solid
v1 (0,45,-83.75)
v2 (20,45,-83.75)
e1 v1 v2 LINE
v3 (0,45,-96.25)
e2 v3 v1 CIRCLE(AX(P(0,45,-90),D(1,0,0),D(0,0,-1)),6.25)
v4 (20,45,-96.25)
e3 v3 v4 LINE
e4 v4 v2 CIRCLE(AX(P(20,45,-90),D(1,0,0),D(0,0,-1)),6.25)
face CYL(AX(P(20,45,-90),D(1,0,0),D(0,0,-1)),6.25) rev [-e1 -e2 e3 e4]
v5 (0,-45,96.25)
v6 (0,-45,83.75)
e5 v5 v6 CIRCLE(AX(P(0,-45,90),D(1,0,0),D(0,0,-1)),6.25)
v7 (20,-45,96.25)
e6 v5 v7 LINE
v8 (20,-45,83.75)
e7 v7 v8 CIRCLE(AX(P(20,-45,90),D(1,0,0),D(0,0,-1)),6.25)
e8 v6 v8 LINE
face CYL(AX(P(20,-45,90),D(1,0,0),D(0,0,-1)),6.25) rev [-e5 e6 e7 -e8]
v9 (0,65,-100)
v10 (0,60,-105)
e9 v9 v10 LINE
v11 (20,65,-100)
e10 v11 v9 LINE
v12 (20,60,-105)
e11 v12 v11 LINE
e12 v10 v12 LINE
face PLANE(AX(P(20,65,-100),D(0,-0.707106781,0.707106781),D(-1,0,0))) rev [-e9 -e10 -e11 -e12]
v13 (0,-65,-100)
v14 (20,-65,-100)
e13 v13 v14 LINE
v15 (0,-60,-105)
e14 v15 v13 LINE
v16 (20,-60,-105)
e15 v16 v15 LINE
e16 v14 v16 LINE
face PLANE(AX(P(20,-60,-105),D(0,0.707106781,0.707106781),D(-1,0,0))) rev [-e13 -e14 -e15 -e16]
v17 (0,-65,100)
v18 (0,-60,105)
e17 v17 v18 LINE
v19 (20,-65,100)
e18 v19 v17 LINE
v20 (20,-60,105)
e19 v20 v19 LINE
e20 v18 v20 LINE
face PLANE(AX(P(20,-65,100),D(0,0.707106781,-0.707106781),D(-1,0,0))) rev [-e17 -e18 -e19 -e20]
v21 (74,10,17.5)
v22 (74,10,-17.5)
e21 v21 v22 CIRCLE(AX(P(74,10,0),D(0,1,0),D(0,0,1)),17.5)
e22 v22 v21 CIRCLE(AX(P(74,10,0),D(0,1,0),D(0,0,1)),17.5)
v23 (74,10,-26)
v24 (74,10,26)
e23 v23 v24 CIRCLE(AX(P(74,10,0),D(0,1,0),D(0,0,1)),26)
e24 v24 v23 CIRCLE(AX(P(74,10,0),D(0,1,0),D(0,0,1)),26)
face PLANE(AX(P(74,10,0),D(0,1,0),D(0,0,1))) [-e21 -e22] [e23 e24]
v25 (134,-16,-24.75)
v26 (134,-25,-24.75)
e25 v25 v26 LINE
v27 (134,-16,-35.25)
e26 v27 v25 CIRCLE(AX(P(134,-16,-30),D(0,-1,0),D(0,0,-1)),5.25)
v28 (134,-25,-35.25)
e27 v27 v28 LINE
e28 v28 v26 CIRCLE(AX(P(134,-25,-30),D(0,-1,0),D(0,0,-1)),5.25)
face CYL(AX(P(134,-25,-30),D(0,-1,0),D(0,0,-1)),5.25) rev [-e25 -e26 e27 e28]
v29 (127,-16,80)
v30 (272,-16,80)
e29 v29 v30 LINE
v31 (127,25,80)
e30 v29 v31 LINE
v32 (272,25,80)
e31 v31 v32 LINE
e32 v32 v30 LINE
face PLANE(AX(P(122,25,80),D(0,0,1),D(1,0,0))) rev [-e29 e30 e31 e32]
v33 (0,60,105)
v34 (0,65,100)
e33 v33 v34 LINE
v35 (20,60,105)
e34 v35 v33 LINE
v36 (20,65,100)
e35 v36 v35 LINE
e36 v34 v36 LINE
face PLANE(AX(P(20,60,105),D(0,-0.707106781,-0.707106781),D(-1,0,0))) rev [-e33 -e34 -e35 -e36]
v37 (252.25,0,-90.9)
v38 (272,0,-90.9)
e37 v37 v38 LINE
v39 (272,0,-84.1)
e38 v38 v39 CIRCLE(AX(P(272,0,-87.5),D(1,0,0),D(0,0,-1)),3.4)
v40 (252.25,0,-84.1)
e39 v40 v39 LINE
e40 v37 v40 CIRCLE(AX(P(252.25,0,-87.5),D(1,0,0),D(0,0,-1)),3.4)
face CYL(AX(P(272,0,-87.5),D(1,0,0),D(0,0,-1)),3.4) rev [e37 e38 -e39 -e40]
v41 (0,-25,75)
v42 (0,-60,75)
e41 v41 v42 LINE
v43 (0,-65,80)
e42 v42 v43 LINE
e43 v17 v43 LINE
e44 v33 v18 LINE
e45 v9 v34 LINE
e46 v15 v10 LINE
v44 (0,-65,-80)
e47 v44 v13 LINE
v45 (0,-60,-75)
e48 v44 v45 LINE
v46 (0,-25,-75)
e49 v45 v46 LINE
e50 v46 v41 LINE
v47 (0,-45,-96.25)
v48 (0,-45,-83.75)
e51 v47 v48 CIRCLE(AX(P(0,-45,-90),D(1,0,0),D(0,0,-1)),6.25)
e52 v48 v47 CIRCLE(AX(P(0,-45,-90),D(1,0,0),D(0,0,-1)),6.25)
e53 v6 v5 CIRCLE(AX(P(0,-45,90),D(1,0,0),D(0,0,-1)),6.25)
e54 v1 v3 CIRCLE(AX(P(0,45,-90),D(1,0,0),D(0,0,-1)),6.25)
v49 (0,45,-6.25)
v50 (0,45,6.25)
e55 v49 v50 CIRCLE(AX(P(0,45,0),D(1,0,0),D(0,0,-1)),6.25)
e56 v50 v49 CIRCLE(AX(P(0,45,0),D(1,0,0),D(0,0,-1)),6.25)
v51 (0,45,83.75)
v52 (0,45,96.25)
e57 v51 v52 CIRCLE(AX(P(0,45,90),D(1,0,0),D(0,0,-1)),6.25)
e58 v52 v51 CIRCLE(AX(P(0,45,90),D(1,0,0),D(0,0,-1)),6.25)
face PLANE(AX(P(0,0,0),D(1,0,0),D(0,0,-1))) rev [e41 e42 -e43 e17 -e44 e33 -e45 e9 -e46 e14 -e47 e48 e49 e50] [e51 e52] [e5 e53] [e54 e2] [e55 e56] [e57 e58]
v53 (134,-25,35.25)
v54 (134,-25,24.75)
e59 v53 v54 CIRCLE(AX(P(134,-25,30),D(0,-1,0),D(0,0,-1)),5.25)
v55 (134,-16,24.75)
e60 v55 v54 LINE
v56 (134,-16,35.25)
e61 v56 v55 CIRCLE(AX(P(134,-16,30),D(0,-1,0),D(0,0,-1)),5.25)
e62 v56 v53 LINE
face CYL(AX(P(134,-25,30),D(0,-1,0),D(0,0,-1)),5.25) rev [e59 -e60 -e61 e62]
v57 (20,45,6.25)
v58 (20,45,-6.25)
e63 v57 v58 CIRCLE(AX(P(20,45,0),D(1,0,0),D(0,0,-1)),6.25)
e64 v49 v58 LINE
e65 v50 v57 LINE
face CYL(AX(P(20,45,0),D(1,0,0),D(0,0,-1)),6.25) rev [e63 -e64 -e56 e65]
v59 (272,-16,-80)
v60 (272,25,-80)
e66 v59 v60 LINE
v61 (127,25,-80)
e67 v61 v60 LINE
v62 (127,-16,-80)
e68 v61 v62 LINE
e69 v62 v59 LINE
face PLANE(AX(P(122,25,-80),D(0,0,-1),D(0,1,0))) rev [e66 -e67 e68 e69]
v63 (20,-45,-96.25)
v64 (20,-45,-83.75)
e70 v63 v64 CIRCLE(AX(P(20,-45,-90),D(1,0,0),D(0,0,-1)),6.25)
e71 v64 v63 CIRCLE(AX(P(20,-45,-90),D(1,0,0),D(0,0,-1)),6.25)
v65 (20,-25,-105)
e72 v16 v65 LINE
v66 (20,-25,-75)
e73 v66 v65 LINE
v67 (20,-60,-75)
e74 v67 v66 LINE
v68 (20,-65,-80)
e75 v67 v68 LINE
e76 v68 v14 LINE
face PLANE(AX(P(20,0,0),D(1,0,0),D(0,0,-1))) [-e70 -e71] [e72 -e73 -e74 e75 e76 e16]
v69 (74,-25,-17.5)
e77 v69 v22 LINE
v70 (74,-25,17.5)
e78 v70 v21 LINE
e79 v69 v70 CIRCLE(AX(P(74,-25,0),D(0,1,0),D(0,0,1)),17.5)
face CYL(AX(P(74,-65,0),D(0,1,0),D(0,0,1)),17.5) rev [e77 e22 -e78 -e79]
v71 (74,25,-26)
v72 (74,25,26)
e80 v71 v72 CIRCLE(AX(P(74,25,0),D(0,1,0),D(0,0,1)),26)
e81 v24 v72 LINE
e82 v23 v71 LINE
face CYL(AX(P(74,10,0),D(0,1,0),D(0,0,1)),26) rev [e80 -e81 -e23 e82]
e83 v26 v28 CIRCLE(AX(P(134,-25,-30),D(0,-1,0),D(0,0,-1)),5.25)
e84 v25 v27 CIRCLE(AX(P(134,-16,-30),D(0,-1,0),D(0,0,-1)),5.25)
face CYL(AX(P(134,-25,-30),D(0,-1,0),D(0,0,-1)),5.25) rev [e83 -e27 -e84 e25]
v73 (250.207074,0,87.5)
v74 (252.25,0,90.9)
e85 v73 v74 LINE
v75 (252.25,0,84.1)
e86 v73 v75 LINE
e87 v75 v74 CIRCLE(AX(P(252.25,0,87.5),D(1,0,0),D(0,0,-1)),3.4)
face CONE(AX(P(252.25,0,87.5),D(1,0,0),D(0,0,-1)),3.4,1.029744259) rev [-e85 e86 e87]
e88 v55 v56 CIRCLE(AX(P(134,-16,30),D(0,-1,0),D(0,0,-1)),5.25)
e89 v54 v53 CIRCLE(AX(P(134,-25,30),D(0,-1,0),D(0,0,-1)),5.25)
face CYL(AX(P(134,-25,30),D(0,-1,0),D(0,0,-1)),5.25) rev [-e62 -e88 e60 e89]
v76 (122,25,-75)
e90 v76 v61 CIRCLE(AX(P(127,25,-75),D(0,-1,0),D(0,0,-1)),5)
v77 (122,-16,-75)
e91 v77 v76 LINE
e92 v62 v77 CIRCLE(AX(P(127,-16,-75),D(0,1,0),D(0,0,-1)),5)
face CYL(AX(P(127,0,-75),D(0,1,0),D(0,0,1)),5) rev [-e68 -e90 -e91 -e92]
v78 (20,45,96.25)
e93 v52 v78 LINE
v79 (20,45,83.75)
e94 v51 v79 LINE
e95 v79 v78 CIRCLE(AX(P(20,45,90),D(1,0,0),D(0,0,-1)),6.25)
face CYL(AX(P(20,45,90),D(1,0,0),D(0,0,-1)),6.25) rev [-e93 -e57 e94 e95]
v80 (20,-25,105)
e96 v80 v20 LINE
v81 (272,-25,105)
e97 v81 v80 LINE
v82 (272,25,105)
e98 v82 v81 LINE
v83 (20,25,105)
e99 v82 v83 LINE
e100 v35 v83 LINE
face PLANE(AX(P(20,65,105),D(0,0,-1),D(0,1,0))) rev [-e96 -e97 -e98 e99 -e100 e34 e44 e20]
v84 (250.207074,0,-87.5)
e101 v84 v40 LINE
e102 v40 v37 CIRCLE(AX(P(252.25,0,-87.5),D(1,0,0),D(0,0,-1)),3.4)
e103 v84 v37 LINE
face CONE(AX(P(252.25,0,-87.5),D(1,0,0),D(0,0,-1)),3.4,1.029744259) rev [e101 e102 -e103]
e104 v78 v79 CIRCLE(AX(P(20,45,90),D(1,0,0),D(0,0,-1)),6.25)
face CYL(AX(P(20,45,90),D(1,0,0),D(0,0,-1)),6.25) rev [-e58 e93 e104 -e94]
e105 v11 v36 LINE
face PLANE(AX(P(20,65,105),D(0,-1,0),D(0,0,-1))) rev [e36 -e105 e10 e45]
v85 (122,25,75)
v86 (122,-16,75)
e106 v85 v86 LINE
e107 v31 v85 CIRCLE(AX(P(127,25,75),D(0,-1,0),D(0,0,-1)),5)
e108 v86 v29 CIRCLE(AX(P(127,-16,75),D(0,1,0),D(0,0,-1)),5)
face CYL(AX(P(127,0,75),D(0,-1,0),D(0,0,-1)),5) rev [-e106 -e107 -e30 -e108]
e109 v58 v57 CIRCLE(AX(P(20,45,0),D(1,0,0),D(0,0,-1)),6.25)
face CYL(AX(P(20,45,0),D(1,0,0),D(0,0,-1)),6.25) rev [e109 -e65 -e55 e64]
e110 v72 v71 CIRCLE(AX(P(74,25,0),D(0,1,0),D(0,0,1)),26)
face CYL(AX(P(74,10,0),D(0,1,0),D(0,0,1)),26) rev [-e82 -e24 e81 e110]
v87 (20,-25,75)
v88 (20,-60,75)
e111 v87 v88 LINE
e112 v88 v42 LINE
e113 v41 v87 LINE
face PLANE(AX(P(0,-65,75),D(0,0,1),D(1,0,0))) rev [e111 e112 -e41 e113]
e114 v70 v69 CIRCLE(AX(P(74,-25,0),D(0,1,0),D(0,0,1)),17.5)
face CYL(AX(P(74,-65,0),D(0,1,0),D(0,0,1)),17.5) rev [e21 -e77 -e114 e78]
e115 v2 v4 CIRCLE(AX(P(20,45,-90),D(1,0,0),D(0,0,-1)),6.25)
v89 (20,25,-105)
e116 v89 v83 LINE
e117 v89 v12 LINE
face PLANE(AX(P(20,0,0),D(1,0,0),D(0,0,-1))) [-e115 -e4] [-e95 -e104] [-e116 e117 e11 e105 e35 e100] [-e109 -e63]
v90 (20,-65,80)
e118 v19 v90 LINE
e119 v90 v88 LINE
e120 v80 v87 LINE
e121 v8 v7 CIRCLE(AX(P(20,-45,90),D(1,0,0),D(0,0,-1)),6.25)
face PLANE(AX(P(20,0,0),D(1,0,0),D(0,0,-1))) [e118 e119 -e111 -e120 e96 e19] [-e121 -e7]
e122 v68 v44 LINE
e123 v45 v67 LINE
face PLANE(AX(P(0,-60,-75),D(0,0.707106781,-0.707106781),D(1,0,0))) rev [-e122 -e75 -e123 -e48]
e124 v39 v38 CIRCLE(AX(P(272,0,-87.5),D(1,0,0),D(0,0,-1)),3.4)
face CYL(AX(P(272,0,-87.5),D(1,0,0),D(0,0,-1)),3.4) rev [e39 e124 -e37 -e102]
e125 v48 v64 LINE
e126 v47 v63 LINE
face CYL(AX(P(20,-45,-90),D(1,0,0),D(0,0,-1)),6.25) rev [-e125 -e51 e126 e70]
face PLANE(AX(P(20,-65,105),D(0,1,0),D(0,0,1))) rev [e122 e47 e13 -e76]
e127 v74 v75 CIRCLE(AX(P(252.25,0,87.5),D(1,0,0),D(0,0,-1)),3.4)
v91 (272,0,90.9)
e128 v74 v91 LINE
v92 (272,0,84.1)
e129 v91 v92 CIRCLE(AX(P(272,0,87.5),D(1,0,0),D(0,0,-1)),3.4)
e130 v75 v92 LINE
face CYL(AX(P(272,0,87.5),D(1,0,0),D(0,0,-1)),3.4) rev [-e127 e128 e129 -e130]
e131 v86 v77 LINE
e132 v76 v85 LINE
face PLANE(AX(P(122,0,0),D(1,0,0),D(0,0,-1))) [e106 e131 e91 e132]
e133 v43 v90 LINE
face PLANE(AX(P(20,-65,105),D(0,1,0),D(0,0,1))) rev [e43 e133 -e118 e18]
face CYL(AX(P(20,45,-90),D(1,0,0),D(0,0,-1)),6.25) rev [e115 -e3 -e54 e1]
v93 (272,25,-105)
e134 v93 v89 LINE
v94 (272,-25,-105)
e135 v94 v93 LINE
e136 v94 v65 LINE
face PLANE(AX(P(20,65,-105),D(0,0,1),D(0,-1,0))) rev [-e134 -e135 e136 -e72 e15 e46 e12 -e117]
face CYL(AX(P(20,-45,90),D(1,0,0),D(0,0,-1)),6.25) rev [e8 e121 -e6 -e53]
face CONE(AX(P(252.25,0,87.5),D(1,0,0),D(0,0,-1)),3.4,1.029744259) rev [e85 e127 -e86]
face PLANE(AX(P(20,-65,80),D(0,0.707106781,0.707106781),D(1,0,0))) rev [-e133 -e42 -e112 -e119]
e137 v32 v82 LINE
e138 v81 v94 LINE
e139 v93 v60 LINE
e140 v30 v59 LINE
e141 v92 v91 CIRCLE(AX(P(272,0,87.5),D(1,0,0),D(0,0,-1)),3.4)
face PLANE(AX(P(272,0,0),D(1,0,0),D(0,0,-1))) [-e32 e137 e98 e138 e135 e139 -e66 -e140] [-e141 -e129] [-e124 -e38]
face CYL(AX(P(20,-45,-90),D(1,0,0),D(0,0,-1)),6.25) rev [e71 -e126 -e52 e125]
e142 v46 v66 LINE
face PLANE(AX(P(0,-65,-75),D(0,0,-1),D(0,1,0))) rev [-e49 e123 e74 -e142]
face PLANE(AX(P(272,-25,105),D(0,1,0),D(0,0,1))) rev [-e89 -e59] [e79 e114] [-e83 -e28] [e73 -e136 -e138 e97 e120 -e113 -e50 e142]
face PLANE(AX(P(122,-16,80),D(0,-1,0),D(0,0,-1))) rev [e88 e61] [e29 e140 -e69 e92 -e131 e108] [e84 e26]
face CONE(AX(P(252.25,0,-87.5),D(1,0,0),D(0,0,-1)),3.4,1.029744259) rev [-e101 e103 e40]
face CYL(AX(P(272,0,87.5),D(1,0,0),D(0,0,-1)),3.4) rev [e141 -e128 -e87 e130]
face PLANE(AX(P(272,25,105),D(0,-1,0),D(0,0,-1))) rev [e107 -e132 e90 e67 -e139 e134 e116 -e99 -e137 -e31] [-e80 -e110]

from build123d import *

# Parameters (mm, degrees)
SKETCH_1_W                = 210
SKETCH_1_H                = 130
EXTRUDE_1_DEPTH           = 20
SKETCH_2_W                = 210
SKETCH_2_H                = 50
EXTRUDE_2_DEPTH           = 252
SKETCH_3_R                = 26
CUT_EXTRUDE_1_DEPTH       = 15
SKETCH_4_R                = 17.5
CUT_EXTRUDE_2_DEPTH       = 302.054812285
SKETCH_5_W                = 160
SKETCH_5_H                = 41
CUT_EXTRUDE_3_DEPTH       = 150
HOLE_WIZARD_M8_1_D        = 6.8
HOLE_WIZARD_M8_1_DEPTH    = 19.75
HOLE_WIZARD_M8_1_TIP      = 2.042926105
HOLE_WIZARD_10_5_10_5_1_D = 10.5
SKETCH_10_W               = 150
SKETCH_10_H               = 40
CUT_EXTRUDE_4_DEPTH       = 281.631430884
HOLE_WIZARD_12_5_12_5_1_D = 12.5
CHAMFER_1_SIZE            = 5
FILLET_1_R                = 5


with BuildPart() as part:
    # 草图1 → 凸台-拉伸1 (new body)
    with BuildSketch(Plane(origin=(0, 0, 0), x_dir=(0, 0, -1), z_dir=(1, 0, 0))):
        Rectangle(SKETCH_1_W, SKETCH_1_H)
    extrude(amount=EXTRUDE_1_DEPTH)

    # 草图2 → 凸台-拉伸2 (add)
    with BuildSketch(Plane(origin=(20, 0, 0), x_dir=(0, 0, -1), z_dir=(1, 0, 0))):
        Rectangle(SKETCH_2_W, SKETCH_2_H)
    extrude(amount=EXTRUDE_2_DEPTH)

    # 草图3 → 切除-拉伸1 (cut)
    with BuildSketch(Plane(origin=(0, 25, 0), x_dir=(1, 0, 0), z_dir=(0, 1, 0))):
        with Locations(Location((74, 0, 0), (0, 0, 270))):
            Circle(SKETCH_3_R)
    extrude(amount=-CUT_EXTRUDE_1_DEPTH, mode=Mode.SUBTRACT)

    # 草图4 → 切除-拉伸2 (cut, through all)
    with BuildSketch(Plane(origin=(0, 10, 0), x_dir=(1, 0, 0), z_dir=(0, 1, 0))):
        with Locations(Location((74, 0, 0), (0, 0, 270))):
            Circle(SKETCH_4_R)
    extrude(amount=-CUT_EXTRUDE_2_DEPTH, mode=Mode.SUBTRACT)

    # 草图5 → 切除-拉伸3 (cut)
    with BuildSketch(Plane(origin=(272, 0, 0), x_dir=(0, 0, -1), z_dir=(1, 0, 0))):
        with Locations((0, 4.5)):
            Rectangle(SKETCH_5_W, SKETCH_5_H)
    extrude(amount=-CUT_EXTRUDE_3_DEPTH, mode=Mode.SUBTRACT)

    # M8 螺纹孔1
    with Locations(Plane(origin=(272, 0, 0), x_dir=(0, 0, -1), z_dir=(1, 0, 0))):
        with Locations((-87.5, 0), (87.5, 0)):
            Hole(HOLE_WIZARD_M8_1_D / 2, depth=HOLE_WIZARD_M8_1_DEPTH)
            with Locations((0, 0, -(HOLE_WIZARD_M8_1_DEPTH + HOLE_WIZARD_M8_1_TIP / 2))):  # 118° drill point
                Cone(0, HOLE_WIZARD_M8_1_D / 2, HOLE_WIZARD_M8_1_TIP, mode=Mode.SUBTRACT)

    # Ø10.5 (10.5) 直径孔1 (through all)
    with Locations(Plane(origin=(0, -25, 0), x_dir=(-1, 0, 0), z_dir=(0, -1, 0))):
        with Locations((-134, 30), (-134, -30)):
            Hole(HOLE_WIZARD_10_5_10_5_1_D / 2)

    # 草图10 → 切除-拉伸4 (cut, through all)
    with BuildSketch(Plane(origin=(20, 0, 0), x_dir=(0, 0, -1), z_dir=(1, 0, 0))):
        with Locations((0, -45)):
            Rectangle(SKETCH_10_W, SKETCH_10_H)
    extrude(amount=-CUT_EXTRUDE_4_DEPTH, mode=Mode.SUBTRACT)

    # Ø12.5 (12.5) 直径孔1 (through all)
    with Locations(Plane(origin=(20, 0, 0), x_dir=(0, 0, -1), z_dir=(1, 0, 0))):
        with Locations((-90, 45), (0, 45), (90, 45), (-90, -45), (90, -45)):
            Hole(HOLE_WIZARD_12_5_12_5_1_D / 2)

    # 倒角1
    chamfer_1_edges = [part.edges().sort_by_distance(p)[0] for p in [
        (10, -65, -105),
        (10, -65, 105),
        (10, -65, 75),
        (10, 65, 105),
        (10, -65, -75),
        (10, 65, -105),
    ]]
    chamfer(chamfer_1_edges, length=CHAMFER_1_SIZE)

    # 圆角1
    fillet_1_edges = [part.edges().sort_by_distance(p)[0] for p in [
        (122, 4.5, 80),
        (122, 4.5, -80),
    ]]
    fillet(fillet_1_edges, radius=FILLET_1_R)


solid = part.part
